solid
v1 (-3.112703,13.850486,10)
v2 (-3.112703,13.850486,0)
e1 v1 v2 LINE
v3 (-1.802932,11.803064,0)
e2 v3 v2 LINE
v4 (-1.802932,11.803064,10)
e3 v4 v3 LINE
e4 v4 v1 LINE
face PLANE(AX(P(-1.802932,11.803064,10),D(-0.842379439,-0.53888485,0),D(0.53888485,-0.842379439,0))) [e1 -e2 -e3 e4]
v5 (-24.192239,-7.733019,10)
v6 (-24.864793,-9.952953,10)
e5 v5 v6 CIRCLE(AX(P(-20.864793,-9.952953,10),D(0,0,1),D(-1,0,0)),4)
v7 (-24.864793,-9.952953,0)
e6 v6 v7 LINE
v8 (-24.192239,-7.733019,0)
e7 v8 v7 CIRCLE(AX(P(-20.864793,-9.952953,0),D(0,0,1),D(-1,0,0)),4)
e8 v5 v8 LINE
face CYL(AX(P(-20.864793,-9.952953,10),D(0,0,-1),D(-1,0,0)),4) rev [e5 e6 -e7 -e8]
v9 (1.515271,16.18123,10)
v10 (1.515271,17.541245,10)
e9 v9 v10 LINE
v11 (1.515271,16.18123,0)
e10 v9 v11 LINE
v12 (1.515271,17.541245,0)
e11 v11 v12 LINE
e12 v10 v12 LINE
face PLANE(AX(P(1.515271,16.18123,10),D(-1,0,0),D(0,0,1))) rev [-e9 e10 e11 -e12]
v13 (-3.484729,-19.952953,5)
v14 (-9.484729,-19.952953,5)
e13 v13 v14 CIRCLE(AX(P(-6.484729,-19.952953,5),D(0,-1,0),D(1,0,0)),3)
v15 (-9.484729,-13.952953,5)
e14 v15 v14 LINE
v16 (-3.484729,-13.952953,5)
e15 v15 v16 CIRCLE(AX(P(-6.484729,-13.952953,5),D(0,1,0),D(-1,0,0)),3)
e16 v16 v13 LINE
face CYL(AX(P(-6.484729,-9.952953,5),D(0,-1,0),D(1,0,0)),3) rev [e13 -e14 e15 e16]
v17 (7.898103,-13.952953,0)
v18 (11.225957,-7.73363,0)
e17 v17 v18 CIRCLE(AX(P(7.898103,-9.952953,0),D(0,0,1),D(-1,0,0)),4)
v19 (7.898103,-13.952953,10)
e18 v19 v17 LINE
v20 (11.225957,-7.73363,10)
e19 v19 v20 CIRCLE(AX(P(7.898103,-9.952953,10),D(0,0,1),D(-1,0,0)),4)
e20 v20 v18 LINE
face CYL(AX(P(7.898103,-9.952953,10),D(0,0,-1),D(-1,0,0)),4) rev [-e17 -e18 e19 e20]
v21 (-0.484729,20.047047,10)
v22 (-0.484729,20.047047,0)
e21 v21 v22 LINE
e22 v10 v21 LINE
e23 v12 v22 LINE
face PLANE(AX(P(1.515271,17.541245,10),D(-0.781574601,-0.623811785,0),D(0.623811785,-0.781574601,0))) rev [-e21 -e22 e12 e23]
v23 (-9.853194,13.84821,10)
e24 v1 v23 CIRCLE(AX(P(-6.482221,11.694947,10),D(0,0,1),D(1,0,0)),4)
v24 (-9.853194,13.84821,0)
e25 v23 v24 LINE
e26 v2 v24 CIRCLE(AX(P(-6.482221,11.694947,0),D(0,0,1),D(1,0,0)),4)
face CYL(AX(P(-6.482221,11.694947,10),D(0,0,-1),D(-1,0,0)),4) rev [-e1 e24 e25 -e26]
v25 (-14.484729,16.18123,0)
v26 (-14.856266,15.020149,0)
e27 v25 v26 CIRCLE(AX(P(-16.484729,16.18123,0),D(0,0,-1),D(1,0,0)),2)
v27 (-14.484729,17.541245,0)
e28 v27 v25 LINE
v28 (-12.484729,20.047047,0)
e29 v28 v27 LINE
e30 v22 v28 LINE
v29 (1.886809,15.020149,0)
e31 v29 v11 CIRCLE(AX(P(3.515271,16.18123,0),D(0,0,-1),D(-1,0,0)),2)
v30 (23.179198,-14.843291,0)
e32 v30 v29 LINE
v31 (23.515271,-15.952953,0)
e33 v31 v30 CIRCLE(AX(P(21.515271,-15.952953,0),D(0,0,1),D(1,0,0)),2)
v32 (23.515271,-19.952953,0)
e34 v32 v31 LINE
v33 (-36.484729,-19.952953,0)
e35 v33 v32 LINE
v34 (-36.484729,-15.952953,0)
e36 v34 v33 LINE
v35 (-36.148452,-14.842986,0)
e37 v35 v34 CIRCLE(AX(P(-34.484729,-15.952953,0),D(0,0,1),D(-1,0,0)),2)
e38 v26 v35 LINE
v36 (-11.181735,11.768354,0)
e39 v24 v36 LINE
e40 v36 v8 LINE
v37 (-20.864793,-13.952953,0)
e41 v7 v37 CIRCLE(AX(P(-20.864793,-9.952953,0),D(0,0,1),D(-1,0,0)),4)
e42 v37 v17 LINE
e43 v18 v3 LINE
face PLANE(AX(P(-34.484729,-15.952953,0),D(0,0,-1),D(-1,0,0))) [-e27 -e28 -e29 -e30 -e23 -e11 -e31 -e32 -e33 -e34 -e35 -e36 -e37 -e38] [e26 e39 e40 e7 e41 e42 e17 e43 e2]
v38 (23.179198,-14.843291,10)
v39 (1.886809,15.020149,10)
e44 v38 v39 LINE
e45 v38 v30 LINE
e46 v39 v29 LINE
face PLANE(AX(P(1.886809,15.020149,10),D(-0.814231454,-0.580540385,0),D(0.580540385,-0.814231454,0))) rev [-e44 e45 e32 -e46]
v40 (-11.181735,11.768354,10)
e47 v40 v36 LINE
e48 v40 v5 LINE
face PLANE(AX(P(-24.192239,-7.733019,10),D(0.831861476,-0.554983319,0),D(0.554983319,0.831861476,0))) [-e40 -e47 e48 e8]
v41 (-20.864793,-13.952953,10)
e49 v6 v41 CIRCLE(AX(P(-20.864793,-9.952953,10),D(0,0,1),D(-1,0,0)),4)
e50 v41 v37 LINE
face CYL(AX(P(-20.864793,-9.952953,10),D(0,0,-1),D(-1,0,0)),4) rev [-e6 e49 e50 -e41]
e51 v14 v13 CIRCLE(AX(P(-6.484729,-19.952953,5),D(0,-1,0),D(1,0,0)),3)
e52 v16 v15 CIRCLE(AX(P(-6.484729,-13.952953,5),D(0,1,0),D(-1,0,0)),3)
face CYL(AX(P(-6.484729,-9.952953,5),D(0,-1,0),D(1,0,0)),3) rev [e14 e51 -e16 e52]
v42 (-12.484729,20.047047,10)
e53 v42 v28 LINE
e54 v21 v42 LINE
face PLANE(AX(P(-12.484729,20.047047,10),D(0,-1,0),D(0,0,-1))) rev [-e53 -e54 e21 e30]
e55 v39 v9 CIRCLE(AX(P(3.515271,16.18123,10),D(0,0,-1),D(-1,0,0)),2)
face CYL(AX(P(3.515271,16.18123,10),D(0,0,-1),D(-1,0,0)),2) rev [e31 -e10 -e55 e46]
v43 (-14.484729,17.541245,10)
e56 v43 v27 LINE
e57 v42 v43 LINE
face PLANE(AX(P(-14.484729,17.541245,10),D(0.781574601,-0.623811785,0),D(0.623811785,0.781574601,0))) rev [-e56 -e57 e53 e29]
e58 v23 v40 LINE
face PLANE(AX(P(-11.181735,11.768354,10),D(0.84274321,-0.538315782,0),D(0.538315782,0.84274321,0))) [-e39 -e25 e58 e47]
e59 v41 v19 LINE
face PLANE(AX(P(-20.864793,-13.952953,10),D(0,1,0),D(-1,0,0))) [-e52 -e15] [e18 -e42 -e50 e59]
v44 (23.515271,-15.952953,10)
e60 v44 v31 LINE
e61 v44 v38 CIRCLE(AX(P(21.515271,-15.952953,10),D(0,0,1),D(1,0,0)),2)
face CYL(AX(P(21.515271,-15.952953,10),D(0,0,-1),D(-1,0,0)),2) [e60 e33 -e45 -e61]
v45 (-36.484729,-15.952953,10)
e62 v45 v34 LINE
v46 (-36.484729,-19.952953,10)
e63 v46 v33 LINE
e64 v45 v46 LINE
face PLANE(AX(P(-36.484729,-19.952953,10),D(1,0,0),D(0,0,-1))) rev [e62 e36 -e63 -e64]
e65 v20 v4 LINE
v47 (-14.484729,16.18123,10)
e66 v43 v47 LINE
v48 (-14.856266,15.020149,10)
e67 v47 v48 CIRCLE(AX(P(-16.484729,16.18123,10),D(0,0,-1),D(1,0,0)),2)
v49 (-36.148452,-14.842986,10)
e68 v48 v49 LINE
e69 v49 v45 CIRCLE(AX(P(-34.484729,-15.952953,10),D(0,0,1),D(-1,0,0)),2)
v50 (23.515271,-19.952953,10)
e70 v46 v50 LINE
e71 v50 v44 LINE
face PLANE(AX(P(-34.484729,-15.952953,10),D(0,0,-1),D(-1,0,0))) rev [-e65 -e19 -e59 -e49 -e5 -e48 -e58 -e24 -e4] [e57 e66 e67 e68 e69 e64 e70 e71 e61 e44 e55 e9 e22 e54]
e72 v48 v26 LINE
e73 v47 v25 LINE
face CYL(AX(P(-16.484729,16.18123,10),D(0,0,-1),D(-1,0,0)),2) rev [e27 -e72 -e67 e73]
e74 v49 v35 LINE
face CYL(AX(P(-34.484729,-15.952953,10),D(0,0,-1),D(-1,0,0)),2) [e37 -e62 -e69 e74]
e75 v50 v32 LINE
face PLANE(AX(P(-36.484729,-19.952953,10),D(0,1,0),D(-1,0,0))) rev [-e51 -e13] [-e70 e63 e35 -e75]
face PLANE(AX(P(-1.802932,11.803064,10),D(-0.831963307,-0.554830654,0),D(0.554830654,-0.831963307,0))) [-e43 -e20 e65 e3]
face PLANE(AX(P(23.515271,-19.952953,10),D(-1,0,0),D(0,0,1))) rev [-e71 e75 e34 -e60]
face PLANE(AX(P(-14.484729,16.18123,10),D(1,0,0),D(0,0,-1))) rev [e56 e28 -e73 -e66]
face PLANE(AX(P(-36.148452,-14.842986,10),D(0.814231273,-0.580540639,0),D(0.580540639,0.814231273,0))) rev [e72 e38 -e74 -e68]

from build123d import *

# Parameters (mm, degrees)
EXTRUDE_1_DEPTH     = 10
SKETCH_3_R          = 3
CUT_EXTRUDE_1_DEPTH = 10


with BuildPart() as part:
    # 草图1 → 凸台-拉伸1 (new body)
    with BuildSketch(Plane.XY):
        with BuildLine():
            Line((-36.484728771, -19.952952756), (23.515271229, -19.952952756))
            Line((23.515271229, -19.952952756), (23.515271229, -15.952952756))
            ThreePointArc((23.515271229, -15.952952756), (23.429409838, -15.373234389), (23.179197844, -14.843291448))
            Line((23.179197844, -14.843291448), (1.886808682, 15.02014861))
            ThreePointArc((1.886808682, 15.02014861), (1.61041886, 15.571691167), (1.515271229, 16.181229888))
            Line((1.515271229, 16.181229888), (1.515271229, 17.541244626))
            Line((1.515271229, 17.541244626), (-0.484728771, 20.047047244))
            Line((-0.484728771, 20.047047244), (-12.484728771, 20.047047244))
            Line((-12.484728771, 20.047047244), (-14.484728771, 17.541244626))
            Line((-14.484728771, 17.541244626), (-14.484728771, 16.181229888))
            ThreePointArc((-14.484728771, 16.181229888), (-14.579876402, 15.571691167), (-14.856266224, 15.02014861))
            Line((-14.856266224, 15.02014861), (-36.148451723, -14.842986118))
            ThreePointArc((-36.148451723, -14.842986118), (-36.39881418, -15.373058759), (-36.484728771, -15.952952756))
            Line((-36.484728771, -15.952952756), (-36.484728771, -19.952952756))
        make_face()
        with BuildLine():
            Line((-24.192238855, -7.733019479), (-11.181735098, 11.768353778))
            Line((-11.181735098, 11.768353778), (-9.853193624, 13.848209774))
            ThreePointArc((-9.853193624, 13.848209774), (-6.483571586, 15.694946417), (-3.112703027, 13.850486044))
            Line((-3.112703027, 13.850486044), (-1.802931634, 11.803064426))
            Line((-1.802931634, 11.803064426), (11.2259567, -7.733630139))
            ThreePointArc((11.2259567, -7.733630139), (11.424949828, -11.840107961), (7.89810347, -13.952952756))
            Line((7.89810347, -13.952952756), (-20.864792951, -13.952952756))
            ThreePointArc((-20.864792951, -13.952952756), (-24.391812451, -11.839784346), (-24.192238855, -7.733019479))
        make_face(mode=Mode.SUBTRACT)
    extrude(amount=EXTRUDE_1_DEPTH)

    # 草图3 → 切除-拉伸1 (cut)
    with BuildSketch(Plane.XZ.offset(19.952952756)):
        with Locations((-6.484728771, 5)):
            Circle(SKETCH_3_R)
    extrude(amount=-CUT_EXTRUDE_1_DEPTH, mode=Mode.SUBTRACT)


solid = part.part
